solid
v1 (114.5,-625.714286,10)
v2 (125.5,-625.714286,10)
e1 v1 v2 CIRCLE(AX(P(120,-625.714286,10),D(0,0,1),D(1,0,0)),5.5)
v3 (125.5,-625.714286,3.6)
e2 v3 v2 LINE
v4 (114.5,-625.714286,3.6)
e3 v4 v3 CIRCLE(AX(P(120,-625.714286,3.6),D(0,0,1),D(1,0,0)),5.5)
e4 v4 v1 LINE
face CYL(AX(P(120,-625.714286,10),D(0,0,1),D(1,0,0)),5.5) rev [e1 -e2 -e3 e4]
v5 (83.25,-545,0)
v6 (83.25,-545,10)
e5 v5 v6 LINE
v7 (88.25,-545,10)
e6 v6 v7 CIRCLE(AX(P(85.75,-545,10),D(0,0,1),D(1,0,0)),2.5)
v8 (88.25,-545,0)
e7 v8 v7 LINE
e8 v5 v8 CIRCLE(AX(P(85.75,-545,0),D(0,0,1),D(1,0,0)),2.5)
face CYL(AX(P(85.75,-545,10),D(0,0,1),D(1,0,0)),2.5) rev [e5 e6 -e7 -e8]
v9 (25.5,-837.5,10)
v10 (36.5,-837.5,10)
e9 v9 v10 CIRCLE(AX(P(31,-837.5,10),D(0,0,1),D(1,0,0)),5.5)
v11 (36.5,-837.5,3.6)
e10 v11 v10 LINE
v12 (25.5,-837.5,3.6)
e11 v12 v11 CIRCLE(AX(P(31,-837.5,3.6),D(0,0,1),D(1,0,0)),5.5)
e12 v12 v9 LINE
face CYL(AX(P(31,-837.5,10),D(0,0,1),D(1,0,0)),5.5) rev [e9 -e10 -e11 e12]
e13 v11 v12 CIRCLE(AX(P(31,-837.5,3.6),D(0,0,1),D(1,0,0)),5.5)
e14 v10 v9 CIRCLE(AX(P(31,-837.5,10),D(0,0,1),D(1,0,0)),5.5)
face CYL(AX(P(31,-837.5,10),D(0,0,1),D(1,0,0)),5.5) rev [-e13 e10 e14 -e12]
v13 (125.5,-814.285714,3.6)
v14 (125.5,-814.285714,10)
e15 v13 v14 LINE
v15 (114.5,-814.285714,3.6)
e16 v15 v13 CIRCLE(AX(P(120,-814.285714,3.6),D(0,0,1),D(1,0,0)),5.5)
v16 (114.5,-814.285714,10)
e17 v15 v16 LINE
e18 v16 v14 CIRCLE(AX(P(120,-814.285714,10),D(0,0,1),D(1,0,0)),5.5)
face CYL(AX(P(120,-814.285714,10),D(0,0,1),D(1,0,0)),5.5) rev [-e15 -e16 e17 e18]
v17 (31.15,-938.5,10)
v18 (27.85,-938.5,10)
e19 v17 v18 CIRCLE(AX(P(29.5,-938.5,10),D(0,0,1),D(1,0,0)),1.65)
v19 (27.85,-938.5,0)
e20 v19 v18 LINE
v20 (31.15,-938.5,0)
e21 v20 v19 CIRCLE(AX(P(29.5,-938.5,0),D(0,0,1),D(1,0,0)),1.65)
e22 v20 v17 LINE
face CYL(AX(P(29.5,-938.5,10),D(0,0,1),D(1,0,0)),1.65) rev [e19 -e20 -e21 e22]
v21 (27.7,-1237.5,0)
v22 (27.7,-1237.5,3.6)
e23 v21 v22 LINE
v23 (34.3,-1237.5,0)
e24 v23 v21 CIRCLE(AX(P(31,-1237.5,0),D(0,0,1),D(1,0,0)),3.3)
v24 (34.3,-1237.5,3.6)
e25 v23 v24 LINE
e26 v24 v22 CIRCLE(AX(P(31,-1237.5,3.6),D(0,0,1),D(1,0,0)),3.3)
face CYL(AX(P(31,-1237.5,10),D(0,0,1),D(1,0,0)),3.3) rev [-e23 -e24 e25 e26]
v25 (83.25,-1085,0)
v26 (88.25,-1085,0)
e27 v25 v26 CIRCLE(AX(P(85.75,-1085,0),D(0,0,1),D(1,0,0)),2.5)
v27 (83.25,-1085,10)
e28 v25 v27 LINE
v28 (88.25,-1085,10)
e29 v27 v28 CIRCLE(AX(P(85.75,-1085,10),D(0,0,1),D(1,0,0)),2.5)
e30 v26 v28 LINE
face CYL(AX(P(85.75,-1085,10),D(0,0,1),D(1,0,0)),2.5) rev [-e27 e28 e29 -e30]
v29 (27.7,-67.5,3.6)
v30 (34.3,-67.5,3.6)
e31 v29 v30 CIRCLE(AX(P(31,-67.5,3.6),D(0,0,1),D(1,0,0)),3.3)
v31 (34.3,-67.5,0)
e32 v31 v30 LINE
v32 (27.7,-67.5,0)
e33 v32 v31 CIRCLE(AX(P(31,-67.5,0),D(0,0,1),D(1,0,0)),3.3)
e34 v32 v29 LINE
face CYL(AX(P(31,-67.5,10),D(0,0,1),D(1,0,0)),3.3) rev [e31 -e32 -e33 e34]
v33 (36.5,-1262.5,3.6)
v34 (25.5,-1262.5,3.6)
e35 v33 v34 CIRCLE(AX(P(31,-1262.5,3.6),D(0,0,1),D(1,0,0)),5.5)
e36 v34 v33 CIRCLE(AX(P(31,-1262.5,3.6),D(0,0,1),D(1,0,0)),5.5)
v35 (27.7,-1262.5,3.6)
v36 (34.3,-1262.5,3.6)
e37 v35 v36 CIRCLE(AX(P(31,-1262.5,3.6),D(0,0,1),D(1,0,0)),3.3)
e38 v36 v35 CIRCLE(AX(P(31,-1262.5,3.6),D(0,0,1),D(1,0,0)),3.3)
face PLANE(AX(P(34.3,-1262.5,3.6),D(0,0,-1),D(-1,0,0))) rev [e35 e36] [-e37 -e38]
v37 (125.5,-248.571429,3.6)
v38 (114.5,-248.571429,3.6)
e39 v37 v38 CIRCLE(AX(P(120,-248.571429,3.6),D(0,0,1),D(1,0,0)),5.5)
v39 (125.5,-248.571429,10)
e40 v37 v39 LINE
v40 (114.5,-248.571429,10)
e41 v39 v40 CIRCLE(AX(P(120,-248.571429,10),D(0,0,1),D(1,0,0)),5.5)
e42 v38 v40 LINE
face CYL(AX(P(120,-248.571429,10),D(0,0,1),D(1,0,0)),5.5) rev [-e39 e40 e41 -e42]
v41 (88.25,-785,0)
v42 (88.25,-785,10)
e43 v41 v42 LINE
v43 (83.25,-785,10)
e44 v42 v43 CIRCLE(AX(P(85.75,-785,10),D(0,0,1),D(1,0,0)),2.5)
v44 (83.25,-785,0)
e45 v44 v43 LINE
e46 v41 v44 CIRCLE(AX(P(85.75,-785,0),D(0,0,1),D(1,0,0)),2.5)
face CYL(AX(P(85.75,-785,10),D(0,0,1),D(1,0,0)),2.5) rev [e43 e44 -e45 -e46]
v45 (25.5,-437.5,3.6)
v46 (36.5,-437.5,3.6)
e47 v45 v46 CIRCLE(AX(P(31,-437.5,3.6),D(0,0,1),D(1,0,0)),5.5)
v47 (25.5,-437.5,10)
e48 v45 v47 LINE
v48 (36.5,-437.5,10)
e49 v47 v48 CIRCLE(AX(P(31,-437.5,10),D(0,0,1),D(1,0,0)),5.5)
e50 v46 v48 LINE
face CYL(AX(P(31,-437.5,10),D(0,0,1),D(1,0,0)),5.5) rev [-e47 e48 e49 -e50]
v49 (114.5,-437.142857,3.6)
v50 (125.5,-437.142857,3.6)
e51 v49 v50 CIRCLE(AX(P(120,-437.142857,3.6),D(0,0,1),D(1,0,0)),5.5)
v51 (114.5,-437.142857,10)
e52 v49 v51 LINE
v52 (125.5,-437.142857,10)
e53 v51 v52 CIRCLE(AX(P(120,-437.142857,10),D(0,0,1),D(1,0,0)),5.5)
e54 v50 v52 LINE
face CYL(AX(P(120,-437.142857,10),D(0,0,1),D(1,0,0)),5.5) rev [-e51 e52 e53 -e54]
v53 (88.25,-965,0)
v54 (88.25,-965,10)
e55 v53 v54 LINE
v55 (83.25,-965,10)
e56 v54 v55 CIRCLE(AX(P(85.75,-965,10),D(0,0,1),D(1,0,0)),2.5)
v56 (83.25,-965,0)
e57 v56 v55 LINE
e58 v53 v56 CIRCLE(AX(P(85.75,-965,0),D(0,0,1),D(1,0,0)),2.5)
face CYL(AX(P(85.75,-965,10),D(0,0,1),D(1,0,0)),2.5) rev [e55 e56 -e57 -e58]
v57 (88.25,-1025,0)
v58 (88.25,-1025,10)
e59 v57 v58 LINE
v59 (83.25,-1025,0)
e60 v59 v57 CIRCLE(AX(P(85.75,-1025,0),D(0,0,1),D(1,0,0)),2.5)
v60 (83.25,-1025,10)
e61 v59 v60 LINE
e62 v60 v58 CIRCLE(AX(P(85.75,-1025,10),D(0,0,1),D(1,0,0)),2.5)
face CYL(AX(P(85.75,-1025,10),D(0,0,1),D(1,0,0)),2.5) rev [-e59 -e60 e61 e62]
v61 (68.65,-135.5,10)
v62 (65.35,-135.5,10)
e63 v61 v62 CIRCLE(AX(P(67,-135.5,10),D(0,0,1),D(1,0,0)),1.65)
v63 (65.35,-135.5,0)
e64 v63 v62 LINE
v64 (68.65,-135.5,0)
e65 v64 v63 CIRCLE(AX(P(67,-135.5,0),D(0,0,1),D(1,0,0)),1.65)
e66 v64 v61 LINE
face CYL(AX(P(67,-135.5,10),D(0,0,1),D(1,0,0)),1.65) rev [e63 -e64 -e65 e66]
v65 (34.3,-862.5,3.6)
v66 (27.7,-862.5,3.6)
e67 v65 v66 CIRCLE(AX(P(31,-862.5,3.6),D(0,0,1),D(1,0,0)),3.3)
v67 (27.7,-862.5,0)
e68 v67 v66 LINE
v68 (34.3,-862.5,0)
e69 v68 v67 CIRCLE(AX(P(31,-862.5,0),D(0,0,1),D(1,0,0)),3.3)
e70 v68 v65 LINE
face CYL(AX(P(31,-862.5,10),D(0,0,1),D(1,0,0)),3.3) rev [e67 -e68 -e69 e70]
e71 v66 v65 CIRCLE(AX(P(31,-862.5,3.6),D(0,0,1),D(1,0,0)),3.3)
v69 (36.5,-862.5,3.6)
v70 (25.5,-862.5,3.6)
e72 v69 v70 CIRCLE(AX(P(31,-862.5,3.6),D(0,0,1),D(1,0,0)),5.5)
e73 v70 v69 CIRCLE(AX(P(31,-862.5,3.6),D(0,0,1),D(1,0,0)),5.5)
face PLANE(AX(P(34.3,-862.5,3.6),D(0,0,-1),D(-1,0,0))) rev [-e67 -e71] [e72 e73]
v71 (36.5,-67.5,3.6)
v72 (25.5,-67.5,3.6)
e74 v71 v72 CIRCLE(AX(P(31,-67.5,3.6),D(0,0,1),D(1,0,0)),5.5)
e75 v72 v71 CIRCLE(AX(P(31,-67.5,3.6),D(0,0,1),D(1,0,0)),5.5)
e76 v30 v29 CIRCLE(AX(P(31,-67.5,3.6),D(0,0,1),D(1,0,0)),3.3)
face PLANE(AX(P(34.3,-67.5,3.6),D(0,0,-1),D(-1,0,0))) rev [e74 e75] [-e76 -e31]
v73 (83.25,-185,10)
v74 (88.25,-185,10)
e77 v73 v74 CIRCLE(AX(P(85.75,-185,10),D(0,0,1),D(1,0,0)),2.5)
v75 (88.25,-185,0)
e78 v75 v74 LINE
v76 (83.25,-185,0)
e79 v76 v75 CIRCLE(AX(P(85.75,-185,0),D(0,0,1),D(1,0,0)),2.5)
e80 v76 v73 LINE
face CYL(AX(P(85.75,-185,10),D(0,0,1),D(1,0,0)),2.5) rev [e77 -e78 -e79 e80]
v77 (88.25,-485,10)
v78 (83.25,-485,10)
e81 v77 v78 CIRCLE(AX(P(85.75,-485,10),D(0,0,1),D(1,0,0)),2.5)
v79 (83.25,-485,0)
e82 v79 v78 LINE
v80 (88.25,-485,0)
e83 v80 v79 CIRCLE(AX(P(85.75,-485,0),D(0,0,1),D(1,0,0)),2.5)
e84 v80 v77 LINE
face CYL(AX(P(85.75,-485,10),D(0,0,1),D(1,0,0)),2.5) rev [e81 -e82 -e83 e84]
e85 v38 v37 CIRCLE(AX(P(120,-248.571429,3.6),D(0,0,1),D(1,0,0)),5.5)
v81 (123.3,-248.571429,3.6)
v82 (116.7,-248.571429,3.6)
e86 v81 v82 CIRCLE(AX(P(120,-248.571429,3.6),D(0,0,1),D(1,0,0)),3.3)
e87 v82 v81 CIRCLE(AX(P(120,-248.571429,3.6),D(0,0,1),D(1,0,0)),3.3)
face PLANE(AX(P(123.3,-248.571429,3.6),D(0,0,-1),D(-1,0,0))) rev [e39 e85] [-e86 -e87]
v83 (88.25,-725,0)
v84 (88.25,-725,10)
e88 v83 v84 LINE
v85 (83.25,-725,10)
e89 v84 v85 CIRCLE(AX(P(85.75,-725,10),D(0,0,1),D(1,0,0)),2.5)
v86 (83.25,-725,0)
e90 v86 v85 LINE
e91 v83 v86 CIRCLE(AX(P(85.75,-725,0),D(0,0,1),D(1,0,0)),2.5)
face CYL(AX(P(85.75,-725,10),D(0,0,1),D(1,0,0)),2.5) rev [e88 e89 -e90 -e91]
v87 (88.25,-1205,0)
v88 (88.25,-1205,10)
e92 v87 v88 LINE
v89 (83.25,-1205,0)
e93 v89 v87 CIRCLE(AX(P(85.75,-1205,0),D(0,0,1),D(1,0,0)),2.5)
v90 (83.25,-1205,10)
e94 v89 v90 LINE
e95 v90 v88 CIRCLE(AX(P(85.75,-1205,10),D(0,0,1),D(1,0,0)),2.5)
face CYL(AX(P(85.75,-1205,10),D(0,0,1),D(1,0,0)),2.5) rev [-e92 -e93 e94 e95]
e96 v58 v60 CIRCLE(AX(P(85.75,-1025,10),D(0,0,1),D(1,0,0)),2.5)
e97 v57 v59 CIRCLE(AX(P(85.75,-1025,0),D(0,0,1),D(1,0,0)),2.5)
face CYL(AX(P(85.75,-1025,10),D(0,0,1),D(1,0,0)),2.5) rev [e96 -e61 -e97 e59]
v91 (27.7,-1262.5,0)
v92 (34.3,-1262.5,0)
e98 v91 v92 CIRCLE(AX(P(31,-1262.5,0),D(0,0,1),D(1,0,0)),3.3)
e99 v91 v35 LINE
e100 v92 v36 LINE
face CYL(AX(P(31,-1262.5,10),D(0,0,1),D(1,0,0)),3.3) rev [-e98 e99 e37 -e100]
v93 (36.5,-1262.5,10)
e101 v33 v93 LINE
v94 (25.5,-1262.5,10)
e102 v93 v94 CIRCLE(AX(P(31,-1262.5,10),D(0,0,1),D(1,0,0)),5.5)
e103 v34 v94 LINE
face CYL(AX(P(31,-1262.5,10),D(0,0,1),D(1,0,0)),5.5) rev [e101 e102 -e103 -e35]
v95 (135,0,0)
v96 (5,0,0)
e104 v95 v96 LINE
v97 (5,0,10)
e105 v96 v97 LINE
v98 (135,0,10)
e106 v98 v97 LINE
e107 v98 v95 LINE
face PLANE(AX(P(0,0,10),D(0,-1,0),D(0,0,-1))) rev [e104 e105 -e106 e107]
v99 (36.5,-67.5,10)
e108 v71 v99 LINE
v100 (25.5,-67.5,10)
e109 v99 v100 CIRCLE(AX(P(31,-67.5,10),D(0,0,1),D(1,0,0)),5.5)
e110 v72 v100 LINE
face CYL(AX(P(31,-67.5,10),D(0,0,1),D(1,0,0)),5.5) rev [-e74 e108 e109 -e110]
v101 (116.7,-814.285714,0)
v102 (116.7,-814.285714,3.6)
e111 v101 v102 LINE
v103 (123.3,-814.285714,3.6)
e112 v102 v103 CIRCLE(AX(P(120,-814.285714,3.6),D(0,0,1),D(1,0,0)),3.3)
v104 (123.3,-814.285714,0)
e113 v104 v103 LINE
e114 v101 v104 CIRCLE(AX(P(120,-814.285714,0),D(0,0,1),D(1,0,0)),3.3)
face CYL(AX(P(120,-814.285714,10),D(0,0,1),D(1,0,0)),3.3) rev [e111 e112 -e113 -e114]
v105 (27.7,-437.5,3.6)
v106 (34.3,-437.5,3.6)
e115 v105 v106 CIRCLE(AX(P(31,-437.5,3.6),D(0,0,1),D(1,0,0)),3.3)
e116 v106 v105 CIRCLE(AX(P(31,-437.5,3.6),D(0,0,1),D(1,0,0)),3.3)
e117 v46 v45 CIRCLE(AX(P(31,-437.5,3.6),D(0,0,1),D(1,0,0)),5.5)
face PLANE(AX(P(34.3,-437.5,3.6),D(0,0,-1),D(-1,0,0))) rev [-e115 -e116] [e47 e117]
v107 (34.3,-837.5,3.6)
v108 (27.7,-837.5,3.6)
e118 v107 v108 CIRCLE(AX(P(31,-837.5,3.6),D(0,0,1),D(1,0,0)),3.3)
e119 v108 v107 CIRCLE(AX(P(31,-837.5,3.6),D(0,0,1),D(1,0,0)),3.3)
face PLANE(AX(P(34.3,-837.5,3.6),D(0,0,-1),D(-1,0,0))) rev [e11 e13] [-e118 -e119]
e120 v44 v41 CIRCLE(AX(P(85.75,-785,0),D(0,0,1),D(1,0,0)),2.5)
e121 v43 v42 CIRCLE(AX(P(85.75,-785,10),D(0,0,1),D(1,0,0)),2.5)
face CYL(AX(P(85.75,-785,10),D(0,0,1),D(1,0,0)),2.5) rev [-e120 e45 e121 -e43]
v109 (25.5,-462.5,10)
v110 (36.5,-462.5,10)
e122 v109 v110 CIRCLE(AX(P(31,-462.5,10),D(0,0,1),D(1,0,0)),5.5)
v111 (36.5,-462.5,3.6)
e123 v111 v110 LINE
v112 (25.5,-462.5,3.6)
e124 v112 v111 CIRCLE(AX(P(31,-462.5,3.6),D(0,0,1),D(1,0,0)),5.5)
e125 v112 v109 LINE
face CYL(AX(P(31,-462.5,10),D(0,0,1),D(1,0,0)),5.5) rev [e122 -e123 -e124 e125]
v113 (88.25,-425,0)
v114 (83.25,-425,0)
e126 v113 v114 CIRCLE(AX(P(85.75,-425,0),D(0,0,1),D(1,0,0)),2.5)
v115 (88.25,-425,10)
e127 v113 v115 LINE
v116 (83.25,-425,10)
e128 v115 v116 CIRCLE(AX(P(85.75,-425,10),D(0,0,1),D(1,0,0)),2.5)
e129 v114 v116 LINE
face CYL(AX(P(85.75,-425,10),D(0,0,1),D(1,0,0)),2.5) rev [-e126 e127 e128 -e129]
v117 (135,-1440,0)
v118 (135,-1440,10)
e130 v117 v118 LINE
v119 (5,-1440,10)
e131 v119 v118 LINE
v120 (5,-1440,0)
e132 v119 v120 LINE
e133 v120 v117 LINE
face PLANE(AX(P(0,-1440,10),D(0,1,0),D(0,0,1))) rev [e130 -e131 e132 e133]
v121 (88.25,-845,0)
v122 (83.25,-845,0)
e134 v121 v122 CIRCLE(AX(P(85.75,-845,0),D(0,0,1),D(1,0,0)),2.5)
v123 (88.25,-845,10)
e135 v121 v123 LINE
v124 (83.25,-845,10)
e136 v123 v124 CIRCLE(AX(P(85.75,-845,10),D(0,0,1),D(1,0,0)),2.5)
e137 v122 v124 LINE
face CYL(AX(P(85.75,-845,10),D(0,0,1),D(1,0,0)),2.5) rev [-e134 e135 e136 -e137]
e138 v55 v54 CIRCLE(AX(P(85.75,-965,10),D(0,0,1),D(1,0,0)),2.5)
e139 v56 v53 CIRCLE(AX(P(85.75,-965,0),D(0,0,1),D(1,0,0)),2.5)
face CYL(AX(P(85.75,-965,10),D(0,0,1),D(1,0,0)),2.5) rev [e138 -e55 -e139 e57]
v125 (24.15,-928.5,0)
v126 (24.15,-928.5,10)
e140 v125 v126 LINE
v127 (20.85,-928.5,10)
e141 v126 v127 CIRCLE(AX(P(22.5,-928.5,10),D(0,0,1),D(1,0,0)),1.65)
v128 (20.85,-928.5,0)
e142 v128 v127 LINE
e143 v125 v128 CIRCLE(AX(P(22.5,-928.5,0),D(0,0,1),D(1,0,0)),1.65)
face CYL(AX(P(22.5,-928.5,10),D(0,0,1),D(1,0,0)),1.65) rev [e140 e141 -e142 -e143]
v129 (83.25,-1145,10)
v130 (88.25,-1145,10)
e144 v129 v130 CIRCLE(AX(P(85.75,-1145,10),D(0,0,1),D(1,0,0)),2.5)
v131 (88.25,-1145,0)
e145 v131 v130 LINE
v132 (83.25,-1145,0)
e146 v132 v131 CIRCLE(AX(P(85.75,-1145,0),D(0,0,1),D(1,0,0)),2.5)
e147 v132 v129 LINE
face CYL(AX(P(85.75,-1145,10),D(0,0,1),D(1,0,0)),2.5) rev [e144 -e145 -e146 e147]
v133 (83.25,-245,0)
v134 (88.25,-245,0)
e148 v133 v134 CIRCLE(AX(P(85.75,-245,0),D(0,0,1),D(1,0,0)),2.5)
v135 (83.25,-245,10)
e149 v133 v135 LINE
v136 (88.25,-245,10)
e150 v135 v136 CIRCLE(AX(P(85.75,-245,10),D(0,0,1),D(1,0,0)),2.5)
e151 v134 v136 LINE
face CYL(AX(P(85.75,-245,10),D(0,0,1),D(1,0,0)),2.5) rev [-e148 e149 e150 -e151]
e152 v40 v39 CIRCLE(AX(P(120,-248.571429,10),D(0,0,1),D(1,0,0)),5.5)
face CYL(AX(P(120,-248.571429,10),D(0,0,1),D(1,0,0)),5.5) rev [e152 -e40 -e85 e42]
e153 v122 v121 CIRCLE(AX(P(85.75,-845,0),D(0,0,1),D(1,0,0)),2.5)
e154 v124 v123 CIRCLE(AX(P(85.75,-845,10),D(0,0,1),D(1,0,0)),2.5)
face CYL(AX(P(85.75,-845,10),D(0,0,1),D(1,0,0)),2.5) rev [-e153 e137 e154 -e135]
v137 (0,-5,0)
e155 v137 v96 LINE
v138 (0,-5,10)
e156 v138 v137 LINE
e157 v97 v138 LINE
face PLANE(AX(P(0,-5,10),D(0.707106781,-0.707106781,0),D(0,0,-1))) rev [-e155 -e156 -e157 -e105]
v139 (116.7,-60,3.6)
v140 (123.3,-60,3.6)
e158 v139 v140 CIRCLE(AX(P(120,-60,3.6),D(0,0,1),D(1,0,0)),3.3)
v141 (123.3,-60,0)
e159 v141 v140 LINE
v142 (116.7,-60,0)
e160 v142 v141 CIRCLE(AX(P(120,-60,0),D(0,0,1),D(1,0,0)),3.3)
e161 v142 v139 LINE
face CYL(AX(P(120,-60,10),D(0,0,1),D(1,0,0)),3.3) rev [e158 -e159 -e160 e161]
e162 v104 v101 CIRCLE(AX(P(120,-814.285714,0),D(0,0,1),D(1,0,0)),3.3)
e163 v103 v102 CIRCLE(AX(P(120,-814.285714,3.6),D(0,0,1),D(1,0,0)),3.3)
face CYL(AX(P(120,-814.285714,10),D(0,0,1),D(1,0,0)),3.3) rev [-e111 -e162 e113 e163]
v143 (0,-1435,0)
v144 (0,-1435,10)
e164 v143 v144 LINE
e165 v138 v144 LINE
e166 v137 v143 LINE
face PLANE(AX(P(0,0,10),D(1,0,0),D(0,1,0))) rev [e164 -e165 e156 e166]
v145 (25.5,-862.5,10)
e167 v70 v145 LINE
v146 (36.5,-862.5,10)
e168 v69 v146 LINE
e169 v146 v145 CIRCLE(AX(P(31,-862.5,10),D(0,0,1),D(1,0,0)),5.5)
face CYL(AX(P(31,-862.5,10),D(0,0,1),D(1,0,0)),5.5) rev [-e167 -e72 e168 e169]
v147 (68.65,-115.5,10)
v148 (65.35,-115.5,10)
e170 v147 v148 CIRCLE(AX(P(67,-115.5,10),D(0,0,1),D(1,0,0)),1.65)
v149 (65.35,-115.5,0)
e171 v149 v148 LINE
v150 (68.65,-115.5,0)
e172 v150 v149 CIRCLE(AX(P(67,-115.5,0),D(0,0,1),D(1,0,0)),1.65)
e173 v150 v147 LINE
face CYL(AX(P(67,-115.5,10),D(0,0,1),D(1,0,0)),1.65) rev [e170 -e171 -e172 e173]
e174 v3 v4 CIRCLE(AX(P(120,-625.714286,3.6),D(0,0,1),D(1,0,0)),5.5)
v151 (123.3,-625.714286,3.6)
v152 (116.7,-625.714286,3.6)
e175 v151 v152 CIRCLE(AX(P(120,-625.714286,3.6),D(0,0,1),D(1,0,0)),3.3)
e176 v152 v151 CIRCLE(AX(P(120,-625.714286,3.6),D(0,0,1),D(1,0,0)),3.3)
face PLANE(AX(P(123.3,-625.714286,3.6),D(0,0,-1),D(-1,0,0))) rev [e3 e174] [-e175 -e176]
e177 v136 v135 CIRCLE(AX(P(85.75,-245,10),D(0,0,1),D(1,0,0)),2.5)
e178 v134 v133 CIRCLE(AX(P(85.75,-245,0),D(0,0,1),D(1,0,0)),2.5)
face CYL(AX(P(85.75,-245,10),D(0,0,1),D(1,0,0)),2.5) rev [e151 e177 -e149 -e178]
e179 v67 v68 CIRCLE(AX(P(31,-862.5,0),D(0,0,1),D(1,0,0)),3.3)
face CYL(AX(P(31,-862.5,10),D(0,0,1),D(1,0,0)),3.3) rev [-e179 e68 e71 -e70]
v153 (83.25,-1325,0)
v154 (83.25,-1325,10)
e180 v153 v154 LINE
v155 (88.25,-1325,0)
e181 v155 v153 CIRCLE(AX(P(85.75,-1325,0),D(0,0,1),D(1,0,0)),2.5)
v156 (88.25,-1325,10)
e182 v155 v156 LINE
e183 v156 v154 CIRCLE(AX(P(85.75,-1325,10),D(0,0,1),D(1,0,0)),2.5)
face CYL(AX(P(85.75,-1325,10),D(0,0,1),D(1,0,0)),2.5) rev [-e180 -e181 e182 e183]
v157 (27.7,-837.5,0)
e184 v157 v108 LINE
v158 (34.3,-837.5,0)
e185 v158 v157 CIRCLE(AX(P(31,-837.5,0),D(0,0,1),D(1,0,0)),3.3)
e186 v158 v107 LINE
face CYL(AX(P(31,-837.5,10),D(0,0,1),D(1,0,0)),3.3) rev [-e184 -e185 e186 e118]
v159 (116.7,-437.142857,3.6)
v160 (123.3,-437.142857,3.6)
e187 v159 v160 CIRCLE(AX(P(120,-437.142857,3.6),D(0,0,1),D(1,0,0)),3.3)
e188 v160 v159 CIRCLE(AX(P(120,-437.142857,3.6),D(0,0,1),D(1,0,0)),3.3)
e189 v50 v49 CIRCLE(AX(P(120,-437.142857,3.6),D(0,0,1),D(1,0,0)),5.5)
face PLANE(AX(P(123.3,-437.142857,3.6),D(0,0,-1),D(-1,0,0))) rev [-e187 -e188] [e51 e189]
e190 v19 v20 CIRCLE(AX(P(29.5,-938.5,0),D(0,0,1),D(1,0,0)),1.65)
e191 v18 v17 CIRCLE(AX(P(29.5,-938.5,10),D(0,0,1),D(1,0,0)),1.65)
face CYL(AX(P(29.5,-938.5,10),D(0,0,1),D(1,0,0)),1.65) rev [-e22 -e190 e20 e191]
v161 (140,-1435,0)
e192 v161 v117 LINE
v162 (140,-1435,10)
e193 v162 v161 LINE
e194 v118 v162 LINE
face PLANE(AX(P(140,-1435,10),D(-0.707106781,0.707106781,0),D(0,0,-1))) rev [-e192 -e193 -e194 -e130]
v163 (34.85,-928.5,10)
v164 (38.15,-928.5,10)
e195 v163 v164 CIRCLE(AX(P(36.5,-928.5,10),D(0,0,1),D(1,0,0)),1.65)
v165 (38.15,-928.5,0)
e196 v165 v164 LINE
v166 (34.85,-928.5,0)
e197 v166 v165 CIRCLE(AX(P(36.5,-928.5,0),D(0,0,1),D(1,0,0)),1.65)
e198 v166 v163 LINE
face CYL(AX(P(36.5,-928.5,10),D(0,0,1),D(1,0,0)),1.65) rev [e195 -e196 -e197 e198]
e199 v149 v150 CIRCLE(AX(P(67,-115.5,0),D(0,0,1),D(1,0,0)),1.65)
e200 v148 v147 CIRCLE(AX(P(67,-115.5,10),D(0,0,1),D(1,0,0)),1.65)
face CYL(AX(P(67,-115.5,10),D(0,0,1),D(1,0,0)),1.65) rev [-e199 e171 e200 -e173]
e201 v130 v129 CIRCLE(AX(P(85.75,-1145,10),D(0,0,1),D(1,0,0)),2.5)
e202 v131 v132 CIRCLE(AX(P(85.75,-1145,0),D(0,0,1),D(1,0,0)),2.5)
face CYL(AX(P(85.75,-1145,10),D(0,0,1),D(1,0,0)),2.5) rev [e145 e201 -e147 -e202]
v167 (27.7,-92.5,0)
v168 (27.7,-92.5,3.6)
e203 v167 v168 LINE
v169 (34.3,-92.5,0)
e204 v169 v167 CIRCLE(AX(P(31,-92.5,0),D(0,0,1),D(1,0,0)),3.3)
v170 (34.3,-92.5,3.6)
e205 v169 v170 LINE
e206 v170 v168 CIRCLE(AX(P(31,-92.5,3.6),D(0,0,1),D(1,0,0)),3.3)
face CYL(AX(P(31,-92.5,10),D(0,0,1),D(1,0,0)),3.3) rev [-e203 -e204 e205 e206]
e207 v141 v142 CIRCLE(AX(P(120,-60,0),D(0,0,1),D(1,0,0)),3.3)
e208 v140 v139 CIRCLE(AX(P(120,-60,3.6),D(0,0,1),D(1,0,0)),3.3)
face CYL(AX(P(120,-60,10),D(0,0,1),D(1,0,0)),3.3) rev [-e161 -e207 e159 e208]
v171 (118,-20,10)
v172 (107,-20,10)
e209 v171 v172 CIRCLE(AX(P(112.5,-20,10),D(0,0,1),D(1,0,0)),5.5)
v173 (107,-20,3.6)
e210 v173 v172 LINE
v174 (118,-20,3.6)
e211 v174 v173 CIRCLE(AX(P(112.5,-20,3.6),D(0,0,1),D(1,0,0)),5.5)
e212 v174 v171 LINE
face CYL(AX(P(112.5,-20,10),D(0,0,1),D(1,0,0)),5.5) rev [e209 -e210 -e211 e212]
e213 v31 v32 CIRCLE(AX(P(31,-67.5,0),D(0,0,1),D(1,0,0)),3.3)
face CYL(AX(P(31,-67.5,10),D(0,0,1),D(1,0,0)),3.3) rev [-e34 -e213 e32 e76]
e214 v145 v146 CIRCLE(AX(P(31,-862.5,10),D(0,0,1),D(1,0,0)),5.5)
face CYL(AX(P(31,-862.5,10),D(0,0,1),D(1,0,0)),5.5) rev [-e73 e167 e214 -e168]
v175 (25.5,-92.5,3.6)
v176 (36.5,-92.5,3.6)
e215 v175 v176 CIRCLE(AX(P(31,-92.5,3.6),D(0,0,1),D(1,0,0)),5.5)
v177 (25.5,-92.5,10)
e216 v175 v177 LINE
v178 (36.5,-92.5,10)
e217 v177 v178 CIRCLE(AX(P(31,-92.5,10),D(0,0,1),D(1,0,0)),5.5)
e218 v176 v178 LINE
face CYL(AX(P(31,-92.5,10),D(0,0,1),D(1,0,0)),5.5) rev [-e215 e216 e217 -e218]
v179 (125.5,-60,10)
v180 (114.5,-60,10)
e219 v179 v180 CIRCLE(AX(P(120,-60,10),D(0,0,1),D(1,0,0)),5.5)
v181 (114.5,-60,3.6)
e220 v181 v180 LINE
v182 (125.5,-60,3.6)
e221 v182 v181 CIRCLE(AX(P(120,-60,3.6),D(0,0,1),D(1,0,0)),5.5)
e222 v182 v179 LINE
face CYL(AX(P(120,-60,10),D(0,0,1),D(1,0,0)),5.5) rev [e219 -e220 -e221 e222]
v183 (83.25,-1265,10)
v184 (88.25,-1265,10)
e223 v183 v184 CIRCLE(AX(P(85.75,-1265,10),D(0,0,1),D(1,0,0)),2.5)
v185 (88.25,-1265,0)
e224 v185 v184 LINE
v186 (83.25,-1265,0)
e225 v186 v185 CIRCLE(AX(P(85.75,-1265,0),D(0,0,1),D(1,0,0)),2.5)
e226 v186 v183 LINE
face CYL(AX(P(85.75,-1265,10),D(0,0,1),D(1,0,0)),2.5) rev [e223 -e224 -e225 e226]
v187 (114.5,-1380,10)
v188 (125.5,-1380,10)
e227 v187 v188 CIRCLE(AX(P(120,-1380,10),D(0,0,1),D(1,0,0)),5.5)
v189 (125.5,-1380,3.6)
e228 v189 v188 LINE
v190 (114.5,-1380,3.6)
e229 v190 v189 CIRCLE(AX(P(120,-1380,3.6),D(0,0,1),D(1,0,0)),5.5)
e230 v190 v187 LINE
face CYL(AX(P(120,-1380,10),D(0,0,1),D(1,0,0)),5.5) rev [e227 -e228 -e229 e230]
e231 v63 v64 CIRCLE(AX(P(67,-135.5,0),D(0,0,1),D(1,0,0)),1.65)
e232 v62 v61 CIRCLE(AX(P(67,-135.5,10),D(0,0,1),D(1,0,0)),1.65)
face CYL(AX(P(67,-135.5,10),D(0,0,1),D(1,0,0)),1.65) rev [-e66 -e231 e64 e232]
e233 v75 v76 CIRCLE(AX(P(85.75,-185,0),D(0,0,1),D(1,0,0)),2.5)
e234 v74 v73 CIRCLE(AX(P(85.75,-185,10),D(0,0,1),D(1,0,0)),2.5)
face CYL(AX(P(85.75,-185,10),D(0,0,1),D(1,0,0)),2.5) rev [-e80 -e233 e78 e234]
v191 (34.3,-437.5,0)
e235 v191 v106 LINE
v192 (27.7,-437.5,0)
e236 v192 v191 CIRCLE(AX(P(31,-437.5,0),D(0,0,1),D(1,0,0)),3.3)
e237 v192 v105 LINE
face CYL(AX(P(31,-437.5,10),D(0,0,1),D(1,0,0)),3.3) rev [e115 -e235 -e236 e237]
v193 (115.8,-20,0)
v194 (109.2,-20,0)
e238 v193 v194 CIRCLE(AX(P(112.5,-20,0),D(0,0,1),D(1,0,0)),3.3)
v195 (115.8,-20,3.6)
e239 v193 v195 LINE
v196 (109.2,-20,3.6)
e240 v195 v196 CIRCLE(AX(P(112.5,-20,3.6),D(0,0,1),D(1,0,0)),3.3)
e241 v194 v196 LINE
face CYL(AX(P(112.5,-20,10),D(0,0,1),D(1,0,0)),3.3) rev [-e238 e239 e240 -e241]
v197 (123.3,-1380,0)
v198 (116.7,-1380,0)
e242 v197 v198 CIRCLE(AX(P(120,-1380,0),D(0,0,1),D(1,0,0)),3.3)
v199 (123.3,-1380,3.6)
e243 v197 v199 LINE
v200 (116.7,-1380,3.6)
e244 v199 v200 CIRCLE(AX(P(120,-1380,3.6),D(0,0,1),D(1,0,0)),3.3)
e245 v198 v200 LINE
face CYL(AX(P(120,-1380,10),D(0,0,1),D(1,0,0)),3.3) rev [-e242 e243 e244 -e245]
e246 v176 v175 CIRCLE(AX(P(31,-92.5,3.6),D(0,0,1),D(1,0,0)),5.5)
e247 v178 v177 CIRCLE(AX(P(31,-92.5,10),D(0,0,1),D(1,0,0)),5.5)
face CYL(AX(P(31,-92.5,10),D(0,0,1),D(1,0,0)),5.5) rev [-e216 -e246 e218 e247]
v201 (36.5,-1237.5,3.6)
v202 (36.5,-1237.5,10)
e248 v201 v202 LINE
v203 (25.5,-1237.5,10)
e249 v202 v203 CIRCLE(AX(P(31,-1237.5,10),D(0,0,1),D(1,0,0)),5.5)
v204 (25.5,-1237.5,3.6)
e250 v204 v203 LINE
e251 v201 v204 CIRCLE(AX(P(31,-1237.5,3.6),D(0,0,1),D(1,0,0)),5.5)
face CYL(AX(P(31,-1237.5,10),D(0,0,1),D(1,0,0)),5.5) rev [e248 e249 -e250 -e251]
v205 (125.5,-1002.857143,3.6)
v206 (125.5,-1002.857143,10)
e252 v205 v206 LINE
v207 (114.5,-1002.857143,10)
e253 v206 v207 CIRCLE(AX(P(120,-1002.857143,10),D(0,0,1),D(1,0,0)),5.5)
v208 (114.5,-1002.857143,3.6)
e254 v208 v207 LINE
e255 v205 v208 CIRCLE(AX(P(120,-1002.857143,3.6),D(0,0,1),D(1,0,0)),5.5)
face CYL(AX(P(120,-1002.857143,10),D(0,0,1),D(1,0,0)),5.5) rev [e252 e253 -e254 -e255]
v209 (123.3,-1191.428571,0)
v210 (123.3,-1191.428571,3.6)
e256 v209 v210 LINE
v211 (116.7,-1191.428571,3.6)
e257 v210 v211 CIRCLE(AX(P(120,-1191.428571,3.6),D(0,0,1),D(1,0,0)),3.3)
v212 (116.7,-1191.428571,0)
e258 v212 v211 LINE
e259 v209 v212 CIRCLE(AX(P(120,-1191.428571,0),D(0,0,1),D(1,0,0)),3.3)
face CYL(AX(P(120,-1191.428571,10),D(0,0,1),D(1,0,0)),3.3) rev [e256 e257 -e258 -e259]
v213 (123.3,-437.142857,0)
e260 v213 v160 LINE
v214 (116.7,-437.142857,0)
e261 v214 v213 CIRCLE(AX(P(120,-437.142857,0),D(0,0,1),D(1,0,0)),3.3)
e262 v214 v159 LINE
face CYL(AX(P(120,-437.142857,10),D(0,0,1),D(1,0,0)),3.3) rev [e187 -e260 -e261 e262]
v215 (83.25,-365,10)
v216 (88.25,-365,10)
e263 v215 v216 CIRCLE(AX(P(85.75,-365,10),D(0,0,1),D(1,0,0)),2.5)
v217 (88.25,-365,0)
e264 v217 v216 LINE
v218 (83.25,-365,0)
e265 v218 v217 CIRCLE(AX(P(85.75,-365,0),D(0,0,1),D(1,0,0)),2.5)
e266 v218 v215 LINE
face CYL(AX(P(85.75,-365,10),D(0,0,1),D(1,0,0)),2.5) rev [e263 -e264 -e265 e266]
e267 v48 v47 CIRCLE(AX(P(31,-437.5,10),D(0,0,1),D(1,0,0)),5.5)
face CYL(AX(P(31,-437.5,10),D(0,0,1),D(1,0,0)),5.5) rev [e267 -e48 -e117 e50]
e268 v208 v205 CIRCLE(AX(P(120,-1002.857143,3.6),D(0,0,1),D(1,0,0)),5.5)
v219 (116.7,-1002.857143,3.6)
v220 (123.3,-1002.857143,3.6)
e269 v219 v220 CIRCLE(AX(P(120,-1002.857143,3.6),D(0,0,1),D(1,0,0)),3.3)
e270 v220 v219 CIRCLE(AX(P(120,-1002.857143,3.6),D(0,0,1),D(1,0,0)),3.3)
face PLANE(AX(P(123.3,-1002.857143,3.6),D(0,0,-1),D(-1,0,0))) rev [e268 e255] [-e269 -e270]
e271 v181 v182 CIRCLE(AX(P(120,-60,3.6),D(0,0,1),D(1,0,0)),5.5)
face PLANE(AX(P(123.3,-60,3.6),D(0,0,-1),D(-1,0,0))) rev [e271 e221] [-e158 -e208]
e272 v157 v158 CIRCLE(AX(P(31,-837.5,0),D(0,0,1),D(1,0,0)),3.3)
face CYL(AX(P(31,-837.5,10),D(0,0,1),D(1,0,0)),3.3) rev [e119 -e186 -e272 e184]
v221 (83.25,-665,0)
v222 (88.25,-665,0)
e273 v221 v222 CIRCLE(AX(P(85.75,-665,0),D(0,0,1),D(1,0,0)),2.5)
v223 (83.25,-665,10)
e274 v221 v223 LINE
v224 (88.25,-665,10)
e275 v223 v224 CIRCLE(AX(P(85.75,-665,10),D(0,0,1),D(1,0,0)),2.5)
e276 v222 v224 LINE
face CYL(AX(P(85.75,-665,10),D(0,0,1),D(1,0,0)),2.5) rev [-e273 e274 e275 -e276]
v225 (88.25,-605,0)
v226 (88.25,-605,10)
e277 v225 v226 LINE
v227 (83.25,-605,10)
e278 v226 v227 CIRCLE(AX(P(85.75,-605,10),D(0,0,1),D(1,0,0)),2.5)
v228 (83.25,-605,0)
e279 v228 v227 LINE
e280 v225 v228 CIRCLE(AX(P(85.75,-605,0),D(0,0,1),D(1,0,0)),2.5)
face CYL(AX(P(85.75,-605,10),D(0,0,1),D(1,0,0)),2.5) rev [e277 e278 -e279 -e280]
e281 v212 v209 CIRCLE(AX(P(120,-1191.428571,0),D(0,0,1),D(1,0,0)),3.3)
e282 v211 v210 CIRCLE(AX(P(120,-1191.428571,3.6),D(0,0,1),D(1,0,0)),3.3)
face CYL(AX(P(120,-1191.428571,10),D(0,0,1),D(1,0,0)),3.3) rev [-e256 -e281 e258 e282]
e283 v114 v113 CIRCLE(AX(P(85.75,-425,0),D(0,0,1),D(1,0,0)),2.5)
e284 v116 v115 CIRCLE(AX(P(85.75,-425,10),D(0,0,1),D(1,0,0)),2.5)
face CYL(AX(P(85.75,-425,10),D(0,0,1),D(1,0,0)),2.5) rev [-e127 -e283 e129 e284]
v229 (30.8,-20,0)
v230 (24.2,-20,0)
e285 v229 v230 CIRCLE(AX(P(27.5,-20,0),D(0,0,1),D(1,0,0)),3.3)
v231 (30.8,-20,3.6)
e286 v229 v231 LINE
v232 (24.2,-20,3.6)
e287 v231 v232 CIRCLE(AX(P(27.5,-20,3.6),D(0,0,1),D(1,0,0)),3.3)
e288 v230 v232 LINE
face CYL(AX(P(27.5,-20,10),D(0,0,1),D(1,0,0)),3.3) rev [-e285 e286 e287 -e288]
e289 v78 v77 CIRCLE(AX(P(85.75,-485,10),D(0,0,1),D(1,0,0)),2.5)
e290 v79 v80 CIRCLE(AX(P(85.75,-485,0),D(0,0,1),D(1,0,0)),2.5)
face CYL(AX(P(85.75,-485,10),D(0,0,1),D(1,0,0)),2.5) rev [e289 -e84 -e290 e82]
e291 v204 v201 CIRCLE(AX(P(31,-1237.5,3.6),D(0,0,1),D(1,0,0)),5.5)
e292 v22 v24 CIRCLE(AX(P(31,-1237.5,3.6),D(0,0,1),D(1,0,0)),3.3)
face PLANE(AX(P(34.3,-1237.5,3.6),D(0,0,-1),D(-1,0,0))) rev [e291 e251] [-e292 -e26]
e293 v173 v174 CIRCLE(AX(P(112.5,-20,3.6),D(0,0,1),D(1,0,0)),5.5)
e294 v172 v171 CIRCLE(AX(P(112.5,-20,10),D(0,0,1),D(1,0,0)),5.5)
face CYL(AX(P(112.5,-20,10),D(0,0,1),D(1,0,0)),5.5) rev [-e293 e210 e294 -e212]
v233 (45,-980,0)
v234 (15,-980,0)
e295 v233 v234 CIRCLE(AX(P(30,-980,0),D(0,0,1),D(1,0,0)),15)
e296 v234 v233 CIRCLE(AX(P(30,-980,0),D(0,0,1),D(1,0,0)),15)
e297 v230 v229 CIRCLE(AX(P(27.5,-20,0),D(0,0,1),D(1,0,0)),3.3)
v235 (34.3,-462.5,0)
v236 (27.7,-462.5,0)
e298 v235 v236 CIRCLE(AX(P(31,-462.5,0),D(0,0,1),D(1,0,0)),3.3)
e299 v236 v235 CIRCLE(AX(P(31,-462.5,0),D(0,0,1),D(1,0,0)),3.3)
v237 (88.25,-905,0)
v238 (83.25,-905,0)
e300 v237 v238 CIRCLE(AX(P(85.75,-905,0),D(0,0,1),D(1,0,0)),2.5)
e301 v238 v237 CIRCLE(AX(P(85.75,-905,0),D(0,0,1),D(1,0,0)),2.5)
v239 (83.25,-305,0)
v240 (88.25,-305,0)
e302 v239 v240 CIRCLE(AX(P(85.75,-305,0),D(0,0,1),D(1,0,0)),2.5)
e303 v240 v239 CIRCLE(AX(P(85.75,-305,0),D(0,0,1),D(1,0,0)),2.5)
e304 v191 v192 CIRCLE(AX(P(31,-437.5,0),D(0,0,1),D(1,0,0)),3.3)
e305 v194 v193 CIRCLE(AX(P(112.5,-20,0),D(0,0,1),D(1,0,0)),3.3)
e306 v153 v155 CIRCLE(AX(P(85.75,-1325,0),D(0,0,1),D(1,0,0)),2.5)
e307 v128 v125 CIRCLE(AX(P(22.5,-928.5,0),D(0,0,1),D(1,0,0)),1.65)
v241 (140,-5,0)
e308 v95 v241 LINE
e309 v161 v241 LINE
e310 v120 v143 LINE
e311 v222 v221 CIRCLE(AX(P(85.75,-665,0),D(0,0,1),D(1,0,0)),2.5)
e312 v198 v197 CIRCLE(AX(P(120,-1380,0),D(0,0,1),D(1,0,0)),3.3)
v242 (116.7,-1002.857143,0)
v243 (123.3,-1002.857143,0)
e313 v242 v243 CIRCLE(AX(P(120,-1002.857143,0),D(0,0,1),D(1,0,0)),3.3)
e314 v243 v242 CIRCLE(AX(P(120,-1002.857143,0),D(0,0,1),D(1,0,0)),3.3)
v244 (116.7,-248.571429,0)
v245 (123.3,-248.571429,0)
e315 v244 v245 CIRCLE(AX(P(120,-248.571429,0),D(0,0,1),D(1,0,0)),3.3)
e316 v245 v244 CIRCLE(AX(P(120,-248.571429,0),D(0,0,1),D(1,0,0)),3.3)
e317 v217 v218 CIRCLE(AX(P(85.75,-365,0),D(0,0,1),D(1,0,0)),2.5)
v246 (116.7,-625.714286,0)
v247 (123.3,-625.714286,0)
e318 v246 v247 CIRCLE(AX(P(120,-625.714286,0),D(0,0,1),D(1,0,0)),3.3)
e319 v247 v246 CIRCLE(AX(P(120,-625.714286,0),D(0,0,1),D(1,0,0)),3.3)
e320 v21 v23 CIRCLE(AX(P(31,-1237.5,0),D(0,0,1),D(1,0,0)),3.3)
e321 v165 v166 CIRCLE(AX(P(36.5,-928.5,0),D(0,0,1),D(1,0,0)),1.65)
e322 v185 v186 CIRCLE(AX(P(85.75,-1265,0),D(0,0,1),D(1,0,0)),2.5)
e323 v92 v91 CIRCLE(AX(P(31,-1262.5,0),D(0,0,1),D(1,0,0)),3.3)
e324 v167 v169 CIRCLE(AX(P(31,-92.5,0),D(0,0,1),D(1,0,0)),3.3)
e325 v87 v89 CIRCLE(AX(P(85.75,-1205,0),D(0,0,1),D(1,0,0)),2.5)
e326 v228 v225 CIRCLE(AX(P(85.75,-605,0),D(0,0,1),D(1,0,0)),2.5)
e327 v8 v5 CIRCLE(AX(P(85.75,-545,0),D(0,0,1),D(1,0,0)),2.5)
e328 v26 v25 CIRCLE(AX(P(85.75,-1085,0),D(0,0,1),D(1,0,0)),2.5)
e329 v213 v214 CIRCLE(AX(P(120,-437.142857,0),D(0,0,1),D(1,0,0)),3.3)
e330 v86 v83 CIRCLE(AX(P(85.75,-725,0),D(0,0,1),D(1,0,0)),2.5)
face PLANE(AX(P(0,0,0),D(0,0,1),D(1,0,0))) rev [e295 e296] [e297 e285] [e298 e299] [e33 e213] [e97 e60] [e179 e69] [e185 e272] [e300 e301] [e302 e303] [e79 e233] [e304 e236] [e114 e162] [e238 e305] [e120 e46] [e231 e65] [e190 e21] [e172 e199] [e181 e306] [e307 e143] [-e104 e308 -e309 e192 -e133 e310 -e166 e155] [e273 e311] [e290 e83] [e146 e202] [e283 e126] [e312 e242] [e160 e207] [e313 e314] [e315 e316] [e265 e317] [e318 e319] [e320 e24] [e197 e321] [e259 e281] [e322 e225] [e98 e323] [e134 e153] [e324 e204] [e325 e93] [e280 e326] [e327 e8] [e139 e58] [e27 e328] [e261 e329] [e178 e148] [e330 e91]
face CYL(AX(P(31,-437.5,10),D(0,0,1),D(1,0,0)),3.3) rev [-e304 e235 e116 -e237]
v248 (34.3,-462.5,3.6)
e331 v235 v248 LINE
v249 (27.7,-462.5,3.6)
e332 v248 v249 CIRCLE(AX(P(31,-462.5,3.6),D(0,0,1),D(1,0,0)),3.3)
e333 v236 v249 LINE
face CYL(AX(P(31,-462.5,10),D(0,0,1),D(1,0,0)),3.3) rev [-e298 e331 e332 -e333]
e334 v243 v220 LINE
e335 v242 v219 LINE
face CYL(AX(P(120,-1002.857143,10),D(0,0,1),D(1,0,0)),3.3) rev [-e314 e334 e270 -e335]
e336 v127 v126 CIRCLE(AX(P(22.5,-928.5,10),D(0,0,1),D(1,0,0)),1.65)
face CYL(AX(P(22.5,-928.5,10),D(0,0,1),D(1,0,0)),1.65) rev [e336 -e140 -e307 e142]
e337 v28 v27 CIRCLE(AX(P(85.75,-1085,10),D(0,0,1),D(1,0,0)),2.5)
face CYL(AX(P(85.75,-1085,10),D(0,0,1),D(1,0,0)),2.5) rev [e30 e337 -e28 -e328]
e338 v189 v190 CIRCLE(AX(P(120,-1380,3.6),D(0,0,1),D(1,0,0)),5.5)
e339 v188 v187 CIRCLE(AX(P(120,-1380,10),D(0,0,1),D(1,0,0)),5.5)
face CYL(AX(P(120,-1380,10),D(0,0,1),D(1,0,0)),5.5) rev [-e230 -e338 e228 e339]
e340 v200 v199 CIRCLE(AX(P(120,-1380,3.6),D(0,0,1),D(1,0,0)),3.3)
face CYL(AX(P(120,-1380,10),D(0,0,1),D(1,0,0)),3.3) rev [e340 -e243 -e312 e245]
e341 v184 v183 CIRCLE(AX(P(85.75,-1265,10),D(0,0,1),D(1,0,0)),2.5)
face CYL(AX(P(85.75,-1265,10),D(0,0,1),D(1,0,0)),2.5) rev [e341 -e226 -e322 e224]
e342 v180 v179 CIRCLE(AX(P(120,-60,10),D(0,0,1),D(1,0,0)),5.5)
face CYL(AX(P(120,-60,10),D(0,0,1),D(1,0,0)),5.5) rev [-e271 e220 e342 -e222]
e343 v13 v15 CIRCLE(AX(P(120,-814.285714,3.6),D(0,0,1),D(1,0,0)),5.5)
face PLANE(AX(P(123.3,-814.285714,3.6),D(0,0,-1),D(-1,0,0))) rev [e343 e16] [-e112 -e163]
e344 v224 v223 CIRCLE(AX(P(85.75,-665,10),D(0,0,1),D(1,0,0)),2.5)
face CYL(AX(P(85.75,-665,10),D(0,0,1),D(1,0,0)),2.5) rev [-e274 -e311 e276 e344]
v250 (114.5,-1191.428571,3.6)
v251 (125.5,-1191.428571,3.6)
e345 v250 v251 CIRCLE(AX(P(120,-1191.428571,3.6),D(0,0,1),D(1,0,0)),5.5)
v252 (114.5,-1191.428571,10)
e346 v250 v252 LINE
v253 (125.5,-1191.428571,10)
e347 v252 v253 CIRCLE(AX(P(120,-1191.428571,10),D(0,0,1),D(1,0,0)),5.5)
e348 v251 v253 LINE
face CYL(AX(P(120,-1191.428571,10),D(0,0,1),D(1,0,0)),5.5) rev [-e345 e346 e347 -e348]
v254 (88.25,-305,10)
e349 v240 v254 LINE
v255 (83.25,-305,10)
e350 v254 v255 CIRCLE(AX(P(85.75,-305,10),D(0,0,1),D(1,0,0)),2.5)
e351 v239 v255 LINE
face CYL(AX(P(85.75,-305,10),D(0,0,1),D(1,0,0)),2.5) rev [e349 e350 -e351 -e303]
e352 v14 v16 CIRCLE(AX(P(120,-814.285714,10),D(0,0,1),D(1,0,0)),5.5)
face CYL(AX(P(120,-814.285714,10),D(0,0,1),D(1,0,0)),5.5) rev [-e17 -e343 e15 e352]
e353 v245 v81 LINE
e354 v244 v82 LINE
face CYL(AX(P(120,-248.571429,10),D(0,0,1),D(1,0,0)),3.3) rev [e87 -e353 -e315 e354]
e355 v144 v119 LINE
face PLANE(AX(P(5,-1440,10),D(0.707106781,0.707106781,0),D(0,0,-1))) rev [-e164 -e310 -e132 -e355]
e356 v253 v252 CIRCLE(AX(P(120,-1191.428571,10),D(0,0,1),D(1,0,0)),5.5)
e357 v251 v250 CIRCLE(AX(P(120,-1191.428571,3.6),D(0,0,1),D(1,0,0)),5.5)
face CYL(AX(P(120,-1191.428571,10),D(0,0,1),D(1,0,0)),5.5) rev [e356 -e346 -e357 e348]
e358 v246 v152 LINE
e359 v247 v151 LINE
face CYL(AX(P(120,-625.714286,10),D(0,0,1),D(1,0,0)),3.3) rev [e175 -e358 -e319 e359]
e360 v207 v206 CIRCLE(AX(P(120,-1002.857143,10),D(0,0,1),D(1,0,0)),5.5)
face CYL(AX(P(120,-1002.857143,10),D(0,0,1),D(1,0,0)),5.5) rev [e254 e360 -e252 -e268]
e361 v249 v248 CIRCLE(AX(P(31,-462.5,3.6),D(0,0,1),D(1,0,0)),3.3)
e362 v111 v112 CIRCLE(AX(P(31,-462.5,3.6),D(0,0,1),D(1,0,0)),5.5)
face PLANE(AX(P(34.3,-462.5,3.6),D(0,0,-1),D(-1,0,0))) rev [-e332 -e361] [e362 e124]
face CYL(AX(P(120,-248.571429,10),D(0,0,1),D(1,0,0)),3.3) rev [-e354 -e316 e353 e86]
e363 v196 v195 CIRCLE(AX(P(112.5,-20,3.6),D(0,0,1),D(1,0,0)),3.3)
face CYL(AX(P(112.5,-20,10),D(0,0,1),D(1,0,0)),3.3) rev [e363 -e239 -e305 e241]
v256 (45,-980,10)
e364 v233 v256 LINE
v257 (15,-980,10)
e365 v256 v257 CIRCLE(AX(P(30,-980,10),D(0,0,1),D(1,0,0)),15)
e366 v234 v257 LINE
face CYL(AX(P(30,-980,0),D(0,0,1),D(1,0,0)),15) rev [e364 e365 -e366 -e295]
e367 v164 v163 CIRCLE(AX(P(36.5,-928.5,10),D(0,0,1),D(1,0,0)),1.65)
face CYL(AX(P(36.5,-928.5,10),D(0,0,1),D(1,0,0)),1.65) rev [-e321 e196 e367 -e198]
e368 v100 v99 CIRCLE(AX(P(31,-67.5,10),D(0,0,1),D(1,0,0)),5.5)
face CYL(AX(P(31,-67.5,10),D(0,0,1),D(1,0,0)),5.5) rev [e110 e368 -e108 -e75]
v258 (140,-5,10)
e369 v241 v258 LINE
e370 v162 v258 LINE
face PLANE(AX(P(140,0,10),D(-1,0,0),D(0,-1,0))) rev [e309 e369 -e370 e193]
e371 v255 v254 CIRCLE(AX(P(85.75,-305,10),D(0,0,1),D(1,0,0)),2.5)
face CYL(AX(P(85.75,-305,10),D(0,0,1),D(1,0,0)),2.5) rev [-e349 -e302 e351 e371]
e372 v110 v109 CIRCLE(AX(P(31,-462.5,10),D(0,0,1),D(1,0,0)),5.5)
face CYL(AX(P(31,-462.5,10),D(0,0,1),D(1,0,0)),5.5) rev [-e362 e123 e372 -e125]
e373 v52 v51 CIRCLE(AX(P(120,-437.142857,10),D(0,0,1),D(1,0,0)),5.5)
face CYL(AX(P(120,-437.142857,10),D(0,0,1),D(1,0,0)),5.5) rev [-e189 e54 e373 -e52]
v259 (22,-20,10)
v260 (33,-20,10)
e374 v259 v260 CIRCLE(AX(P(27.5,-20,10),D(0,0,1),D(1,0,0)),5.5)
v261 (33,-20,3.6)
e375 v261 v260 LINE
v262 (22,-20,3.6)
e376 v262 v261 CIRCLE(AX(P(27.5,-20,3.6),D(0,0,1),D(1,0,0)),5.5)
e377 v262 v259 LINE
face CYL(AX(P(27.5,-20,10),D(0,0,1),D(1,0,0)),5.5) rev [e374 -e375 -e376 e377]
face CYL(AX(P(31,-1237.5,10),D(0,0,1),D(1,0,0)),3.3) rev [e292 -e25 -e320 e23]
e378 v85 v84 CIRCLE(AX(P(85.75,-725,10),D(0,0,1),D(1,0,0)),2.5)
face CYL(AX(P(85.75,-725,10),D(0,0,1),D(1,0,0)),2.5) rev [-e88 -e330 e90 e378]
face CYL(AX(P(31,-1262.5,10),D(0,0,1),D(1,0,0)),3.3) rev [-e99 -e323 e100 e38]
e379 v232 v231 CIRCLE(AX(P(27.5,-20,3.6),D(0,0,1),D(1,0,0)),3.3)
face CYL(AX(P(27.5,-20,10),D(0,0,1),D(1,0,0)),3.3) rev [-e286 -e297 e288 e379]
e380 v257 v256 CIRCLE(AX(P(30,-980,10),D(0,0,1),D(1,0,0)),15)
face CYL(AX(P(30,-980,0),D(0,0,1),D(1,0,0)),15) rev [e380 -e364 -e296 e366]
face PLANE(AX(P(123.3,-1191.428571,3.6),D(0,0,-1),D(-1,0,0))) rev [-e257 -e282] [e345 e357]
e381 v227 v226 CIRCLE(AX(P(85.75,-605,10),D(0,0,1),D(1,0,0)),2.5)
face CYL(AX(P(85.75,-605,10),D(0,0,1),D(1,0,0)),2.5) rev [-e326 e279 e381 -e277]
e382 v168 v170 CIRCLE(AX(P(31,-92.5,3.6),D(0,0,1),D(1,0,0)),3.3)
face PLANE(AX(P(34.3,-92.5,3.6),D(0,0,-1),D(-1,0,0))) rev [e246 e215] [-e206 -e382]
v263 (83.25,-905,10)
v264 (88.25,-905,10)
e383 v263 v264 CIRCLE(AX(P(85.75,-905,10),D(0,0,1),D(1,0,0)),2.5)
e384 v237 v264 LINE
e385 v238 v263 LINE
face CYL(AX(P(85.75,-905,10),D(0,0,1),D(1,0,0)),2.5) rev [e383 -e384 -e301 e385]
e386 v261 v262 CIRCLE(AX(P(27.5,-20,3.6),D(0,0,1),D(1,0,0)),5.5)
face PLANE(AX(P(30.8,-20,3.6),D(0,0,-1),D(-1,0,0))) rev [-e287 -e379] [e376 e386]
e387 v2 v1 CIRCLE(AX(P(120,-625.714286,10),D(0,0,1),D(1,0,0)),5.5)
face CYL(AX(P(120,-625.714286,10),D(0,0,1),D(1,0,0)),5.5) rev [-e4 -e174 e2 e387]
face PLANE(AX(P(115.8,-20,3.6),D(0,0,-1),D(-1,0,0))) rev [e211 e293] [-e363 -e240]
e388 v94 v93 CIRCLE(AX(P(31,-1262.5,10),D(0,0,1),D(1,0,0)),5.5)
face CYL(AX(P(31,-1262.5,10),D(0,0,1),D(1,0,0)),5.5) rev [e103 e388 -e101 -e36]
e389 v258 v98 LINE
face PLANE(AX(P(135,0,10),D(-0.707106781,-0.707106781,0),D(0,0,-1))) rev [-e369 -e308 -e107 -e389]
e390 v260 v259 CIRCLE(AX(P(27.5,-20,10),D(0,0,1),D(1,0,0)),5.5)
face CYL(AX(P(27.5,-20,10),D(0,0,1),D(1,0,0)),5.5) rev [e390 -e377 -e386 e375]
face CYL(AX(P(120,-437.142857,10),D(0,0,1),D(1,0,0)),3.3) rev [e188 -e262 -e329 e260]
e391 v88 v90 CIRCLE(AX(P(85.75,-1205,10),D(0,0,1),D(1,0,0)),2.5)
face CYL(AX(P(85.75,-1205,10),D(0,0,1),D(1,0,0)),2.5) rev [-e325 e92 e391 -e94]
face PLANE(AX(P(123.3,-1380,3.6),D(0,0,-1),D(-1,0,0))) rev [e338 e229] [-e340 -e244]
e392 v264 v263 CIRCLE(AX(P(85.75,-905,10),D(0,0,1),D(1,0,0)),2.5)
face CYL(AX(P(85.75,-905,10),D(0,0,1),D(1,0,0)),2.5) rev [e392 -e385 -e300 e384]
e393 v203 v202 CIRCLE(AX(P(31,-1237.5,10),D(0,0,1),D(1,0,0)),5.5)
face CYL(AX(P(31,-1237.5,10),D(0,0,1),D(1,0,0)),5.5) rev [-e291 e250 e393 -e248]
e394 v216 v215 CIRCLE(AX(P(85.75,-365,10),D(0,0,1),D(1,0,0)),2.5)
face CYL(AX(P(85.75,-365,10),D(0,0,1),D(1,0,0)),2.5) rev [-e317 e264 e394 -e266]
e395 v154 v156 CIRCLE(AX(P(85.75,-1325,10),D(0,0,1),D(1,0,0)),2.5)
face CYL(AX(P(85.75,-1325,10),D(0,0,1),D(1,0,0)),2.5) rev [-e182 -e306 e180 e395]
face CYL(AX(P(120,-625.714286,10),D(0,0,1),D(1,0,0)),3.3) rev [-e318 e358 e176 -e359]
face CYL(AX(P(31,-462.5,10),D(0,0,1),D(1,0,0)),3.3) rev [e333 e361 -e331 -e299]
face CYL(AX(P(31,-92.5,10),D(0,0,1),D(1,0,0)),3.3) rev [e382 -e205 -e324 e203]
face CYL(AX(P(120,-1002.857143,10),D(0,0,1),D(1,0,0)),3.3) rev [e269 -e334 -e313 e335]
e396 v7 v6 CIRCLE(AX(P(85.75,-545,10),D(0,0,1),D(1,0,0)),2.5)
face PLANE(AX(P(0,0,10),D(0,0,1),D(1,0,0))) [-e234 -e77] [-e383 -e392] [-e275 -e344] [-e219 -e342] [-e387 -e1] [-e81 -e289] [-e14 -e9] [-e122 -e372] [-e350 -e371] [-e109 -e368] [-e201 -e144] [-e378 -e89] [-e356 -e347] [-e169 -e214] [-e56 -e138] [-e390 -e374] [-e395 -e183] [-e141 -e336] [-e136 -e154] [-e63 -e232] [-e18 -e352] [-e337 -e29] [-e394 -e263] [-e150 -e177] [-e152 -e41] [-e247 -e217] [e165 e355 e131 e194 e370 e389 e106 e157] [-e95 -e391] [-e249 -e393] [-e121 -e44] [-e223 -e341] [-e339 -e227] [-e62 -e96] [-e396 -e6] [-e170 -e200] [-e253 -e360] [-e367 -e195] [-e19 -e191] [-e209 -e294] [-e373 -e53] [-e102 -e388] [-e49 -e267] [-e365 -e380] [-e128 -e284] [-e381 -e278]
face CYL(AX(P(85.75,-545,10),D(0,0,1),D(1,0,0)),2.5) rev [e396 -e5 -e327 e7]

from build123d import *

# Parameters (mm, degrees)
SKETCH_1_W                     = 140
SKETCH_1_H                     = 1440
EXTRUDE_1_DEPTH                = 10
HOLE_WIZARD_M6_1_D             = 5
HOLE_WIZARD_M6_1_2_D           = 6.6
HOLE_WIZARD_M6_1_2_DEPTH       = 17
HOLE_WIZARD_M6_1_2_CBORE_D     = 11
HOLE_WIZARD_M6_1_2_CBORE_DEPTH = 6.4
HOLE_WIZARD_M6_1_2_TIP         = 1.982840043
HOLE_WIZARD_M4_1_D             = 3.3
SKETCH_9_R                     = 15
CUT_EXTRUDE_2_DEPTH            = 10
CHAMFER_1_SIZE                 = 5
HOLE_WIZARD_M6_2_D             = 6.6
HOLE_WIZARD_M6_2_DEPTH         = 17
HOLE_WIZARD_M6_2_CBORE_D       = 11
HOLE_WIZARD_M6_2_CBORE_DEPTH   = 6.4
HOLE_WIZARD_M6_2_TIP           = 1.982840043
HOLE_WIZARD_M4_2_D             = 3.3
HOLE_WIZARD_M4_2_DEPTH         = 11.5
HOLE_WIZARD_M4_2_TIP           = 0.991420021


with BuildPart() as part:
    # 草图1 → 凸台-拉伸1 (new body)
    with BuildSketch(Plane.XY):
        with Locations((70, -720)):
            Rectangle(SKETCH_1_W, SKETCH_1_H)
    extrude(amount=EXTRUDE_1_DEPTH)

    # Hole Wizard M6 _1 (through all)
    with Locations(Plane.XY.offset(10)):
        with Locations((85.75, -185), (85.75, -245), (85.75, -305), (85.75, -365), (85.75, -425), (85.75, -485), (85.75, -545), (85.75, -605), (85.75, -665), (85.75, -725), (85.75, -785), (85.75, -845), (85.75, -905), (85.75, -965), (85.75, -1025), (85.75, -1085), (85.75, -1145), (85.75, -1205), (85.75, -1265), (85.75, -1325)):
            Hole(HOLE_WIZARD_M6_1_D / 2)

    # Hole Wizard M6 _1 2
    with Locations(Plane.XY.offset(10)):
        with Locations((31, -1262.5), (31, -1237.5), (31, -862.5), (31, -837.5), (31, -462.5), (31, -437.5), (31, -92.5), (31, -67.5)):
            CounterBoreHole(HOLE_WIZARD_M6_1_2_D / 2, HOLE_WIZARD_M6_1_2_CBORE_D / 2, HOLE_WIZARD_M6_1_2_CBORE_DEPTH, depth=HOLE_WIZARD_M6_1_2_DEPTH)
            with Locations((0, 0, -(HOLE_WIZARD_M6_1_2_DEPTH + HOLE_WIZARD_M6_1_2_TIP / 2))):  # 118° drill point
                Cone(0, HOLE_WIZARD_M6_1_2_D / 2, HOLE_WIZARD_M6_1_2_TIP, mode=Mode.SUBTRACT)

    # M4 螺纹孔1 (through all)
    with Locations(Plane.XY.offset(10)):
        with Locations((22.5, -928.5), (36.5, -928.5), (29.5, -938.5)):
            Hole(HOLE_WIZARD_M4_1_D / 2)

    # 草图9 → 切除-拉伸2 (cut)
    with BuildSketch(Plane.XY.offset(10)):
        with Locations((30, -980)):
            Circle(SKETCH_9_R)
    extrude(amount=-CUT_EXTRUDE_2_DEPTH, mode=Mode.SUBTRACT)

    # 倒角1
    chamfer_1_edges = [part.edges().sort_by_distance(p)[0] for p in [
        (0, 0, 5),
        (140, 0, 5),
        (140, -1440, 5),
        (0, -1440, 5),
    ]]
    chamfer(chamfer_1_edges, length=CHAMFER_1_SIZE)

    # M6 六角凹头螺钉的柱形沉头孔2
    with Locations(Plane.XY.offset(10)):
        with Locations((120, -1380), (120, -1191.428571429), (120, -1002.857142857), (120, -814.285714286), (120, -625.714285714), (120, -437.142857143), (120, -248.571428571), (120, -60), (27.5, -20), (112.5, -20)):
            CounterBoreHole(HOLE_WIZARD_M6_2_D / 2, HOLE_WIZARD_M6_2_CBORE_D / 2, HOLE_WIZARD_M6_2_CBORE_DEPTH, depth=HOLE_WIZARD_M6_2_DEPTH)
            with Locations((0, 0, -(HOLE_WIZARD_M6_2_DEPTH + HOLE_WIZARD_M6_2_TIP / 2))):  # 118° drill point
                Cone(0, HOLE_WIZARD_M6_2_D / 2, HOLE_WIZARD_M6_2_TIP, mode=Mode.SUBTRACT)

    # M4 螺纹孔2
    with Locations(Plane.XY.offset(10)):
        with Locations((67, -115.5), (67, -135.5)):
            Hole(HOLE_WIZARD_M4_2_D / 2, depth=HOLE_WIZARD_M4_2_DEPTH)
            with Locations((0, 0, -(HOLE_WIZARD_M4_2_DEPTH + HOLE_WIZARD_M4_2_TIP / 2))):  # 118° drill point
                Cone(0, HOLE_WIZARD_M4_2_D / 2, HOLE_WIZARD_M4_2_TIP, mode=Mode.SUBTRACT)


solid = part.part
